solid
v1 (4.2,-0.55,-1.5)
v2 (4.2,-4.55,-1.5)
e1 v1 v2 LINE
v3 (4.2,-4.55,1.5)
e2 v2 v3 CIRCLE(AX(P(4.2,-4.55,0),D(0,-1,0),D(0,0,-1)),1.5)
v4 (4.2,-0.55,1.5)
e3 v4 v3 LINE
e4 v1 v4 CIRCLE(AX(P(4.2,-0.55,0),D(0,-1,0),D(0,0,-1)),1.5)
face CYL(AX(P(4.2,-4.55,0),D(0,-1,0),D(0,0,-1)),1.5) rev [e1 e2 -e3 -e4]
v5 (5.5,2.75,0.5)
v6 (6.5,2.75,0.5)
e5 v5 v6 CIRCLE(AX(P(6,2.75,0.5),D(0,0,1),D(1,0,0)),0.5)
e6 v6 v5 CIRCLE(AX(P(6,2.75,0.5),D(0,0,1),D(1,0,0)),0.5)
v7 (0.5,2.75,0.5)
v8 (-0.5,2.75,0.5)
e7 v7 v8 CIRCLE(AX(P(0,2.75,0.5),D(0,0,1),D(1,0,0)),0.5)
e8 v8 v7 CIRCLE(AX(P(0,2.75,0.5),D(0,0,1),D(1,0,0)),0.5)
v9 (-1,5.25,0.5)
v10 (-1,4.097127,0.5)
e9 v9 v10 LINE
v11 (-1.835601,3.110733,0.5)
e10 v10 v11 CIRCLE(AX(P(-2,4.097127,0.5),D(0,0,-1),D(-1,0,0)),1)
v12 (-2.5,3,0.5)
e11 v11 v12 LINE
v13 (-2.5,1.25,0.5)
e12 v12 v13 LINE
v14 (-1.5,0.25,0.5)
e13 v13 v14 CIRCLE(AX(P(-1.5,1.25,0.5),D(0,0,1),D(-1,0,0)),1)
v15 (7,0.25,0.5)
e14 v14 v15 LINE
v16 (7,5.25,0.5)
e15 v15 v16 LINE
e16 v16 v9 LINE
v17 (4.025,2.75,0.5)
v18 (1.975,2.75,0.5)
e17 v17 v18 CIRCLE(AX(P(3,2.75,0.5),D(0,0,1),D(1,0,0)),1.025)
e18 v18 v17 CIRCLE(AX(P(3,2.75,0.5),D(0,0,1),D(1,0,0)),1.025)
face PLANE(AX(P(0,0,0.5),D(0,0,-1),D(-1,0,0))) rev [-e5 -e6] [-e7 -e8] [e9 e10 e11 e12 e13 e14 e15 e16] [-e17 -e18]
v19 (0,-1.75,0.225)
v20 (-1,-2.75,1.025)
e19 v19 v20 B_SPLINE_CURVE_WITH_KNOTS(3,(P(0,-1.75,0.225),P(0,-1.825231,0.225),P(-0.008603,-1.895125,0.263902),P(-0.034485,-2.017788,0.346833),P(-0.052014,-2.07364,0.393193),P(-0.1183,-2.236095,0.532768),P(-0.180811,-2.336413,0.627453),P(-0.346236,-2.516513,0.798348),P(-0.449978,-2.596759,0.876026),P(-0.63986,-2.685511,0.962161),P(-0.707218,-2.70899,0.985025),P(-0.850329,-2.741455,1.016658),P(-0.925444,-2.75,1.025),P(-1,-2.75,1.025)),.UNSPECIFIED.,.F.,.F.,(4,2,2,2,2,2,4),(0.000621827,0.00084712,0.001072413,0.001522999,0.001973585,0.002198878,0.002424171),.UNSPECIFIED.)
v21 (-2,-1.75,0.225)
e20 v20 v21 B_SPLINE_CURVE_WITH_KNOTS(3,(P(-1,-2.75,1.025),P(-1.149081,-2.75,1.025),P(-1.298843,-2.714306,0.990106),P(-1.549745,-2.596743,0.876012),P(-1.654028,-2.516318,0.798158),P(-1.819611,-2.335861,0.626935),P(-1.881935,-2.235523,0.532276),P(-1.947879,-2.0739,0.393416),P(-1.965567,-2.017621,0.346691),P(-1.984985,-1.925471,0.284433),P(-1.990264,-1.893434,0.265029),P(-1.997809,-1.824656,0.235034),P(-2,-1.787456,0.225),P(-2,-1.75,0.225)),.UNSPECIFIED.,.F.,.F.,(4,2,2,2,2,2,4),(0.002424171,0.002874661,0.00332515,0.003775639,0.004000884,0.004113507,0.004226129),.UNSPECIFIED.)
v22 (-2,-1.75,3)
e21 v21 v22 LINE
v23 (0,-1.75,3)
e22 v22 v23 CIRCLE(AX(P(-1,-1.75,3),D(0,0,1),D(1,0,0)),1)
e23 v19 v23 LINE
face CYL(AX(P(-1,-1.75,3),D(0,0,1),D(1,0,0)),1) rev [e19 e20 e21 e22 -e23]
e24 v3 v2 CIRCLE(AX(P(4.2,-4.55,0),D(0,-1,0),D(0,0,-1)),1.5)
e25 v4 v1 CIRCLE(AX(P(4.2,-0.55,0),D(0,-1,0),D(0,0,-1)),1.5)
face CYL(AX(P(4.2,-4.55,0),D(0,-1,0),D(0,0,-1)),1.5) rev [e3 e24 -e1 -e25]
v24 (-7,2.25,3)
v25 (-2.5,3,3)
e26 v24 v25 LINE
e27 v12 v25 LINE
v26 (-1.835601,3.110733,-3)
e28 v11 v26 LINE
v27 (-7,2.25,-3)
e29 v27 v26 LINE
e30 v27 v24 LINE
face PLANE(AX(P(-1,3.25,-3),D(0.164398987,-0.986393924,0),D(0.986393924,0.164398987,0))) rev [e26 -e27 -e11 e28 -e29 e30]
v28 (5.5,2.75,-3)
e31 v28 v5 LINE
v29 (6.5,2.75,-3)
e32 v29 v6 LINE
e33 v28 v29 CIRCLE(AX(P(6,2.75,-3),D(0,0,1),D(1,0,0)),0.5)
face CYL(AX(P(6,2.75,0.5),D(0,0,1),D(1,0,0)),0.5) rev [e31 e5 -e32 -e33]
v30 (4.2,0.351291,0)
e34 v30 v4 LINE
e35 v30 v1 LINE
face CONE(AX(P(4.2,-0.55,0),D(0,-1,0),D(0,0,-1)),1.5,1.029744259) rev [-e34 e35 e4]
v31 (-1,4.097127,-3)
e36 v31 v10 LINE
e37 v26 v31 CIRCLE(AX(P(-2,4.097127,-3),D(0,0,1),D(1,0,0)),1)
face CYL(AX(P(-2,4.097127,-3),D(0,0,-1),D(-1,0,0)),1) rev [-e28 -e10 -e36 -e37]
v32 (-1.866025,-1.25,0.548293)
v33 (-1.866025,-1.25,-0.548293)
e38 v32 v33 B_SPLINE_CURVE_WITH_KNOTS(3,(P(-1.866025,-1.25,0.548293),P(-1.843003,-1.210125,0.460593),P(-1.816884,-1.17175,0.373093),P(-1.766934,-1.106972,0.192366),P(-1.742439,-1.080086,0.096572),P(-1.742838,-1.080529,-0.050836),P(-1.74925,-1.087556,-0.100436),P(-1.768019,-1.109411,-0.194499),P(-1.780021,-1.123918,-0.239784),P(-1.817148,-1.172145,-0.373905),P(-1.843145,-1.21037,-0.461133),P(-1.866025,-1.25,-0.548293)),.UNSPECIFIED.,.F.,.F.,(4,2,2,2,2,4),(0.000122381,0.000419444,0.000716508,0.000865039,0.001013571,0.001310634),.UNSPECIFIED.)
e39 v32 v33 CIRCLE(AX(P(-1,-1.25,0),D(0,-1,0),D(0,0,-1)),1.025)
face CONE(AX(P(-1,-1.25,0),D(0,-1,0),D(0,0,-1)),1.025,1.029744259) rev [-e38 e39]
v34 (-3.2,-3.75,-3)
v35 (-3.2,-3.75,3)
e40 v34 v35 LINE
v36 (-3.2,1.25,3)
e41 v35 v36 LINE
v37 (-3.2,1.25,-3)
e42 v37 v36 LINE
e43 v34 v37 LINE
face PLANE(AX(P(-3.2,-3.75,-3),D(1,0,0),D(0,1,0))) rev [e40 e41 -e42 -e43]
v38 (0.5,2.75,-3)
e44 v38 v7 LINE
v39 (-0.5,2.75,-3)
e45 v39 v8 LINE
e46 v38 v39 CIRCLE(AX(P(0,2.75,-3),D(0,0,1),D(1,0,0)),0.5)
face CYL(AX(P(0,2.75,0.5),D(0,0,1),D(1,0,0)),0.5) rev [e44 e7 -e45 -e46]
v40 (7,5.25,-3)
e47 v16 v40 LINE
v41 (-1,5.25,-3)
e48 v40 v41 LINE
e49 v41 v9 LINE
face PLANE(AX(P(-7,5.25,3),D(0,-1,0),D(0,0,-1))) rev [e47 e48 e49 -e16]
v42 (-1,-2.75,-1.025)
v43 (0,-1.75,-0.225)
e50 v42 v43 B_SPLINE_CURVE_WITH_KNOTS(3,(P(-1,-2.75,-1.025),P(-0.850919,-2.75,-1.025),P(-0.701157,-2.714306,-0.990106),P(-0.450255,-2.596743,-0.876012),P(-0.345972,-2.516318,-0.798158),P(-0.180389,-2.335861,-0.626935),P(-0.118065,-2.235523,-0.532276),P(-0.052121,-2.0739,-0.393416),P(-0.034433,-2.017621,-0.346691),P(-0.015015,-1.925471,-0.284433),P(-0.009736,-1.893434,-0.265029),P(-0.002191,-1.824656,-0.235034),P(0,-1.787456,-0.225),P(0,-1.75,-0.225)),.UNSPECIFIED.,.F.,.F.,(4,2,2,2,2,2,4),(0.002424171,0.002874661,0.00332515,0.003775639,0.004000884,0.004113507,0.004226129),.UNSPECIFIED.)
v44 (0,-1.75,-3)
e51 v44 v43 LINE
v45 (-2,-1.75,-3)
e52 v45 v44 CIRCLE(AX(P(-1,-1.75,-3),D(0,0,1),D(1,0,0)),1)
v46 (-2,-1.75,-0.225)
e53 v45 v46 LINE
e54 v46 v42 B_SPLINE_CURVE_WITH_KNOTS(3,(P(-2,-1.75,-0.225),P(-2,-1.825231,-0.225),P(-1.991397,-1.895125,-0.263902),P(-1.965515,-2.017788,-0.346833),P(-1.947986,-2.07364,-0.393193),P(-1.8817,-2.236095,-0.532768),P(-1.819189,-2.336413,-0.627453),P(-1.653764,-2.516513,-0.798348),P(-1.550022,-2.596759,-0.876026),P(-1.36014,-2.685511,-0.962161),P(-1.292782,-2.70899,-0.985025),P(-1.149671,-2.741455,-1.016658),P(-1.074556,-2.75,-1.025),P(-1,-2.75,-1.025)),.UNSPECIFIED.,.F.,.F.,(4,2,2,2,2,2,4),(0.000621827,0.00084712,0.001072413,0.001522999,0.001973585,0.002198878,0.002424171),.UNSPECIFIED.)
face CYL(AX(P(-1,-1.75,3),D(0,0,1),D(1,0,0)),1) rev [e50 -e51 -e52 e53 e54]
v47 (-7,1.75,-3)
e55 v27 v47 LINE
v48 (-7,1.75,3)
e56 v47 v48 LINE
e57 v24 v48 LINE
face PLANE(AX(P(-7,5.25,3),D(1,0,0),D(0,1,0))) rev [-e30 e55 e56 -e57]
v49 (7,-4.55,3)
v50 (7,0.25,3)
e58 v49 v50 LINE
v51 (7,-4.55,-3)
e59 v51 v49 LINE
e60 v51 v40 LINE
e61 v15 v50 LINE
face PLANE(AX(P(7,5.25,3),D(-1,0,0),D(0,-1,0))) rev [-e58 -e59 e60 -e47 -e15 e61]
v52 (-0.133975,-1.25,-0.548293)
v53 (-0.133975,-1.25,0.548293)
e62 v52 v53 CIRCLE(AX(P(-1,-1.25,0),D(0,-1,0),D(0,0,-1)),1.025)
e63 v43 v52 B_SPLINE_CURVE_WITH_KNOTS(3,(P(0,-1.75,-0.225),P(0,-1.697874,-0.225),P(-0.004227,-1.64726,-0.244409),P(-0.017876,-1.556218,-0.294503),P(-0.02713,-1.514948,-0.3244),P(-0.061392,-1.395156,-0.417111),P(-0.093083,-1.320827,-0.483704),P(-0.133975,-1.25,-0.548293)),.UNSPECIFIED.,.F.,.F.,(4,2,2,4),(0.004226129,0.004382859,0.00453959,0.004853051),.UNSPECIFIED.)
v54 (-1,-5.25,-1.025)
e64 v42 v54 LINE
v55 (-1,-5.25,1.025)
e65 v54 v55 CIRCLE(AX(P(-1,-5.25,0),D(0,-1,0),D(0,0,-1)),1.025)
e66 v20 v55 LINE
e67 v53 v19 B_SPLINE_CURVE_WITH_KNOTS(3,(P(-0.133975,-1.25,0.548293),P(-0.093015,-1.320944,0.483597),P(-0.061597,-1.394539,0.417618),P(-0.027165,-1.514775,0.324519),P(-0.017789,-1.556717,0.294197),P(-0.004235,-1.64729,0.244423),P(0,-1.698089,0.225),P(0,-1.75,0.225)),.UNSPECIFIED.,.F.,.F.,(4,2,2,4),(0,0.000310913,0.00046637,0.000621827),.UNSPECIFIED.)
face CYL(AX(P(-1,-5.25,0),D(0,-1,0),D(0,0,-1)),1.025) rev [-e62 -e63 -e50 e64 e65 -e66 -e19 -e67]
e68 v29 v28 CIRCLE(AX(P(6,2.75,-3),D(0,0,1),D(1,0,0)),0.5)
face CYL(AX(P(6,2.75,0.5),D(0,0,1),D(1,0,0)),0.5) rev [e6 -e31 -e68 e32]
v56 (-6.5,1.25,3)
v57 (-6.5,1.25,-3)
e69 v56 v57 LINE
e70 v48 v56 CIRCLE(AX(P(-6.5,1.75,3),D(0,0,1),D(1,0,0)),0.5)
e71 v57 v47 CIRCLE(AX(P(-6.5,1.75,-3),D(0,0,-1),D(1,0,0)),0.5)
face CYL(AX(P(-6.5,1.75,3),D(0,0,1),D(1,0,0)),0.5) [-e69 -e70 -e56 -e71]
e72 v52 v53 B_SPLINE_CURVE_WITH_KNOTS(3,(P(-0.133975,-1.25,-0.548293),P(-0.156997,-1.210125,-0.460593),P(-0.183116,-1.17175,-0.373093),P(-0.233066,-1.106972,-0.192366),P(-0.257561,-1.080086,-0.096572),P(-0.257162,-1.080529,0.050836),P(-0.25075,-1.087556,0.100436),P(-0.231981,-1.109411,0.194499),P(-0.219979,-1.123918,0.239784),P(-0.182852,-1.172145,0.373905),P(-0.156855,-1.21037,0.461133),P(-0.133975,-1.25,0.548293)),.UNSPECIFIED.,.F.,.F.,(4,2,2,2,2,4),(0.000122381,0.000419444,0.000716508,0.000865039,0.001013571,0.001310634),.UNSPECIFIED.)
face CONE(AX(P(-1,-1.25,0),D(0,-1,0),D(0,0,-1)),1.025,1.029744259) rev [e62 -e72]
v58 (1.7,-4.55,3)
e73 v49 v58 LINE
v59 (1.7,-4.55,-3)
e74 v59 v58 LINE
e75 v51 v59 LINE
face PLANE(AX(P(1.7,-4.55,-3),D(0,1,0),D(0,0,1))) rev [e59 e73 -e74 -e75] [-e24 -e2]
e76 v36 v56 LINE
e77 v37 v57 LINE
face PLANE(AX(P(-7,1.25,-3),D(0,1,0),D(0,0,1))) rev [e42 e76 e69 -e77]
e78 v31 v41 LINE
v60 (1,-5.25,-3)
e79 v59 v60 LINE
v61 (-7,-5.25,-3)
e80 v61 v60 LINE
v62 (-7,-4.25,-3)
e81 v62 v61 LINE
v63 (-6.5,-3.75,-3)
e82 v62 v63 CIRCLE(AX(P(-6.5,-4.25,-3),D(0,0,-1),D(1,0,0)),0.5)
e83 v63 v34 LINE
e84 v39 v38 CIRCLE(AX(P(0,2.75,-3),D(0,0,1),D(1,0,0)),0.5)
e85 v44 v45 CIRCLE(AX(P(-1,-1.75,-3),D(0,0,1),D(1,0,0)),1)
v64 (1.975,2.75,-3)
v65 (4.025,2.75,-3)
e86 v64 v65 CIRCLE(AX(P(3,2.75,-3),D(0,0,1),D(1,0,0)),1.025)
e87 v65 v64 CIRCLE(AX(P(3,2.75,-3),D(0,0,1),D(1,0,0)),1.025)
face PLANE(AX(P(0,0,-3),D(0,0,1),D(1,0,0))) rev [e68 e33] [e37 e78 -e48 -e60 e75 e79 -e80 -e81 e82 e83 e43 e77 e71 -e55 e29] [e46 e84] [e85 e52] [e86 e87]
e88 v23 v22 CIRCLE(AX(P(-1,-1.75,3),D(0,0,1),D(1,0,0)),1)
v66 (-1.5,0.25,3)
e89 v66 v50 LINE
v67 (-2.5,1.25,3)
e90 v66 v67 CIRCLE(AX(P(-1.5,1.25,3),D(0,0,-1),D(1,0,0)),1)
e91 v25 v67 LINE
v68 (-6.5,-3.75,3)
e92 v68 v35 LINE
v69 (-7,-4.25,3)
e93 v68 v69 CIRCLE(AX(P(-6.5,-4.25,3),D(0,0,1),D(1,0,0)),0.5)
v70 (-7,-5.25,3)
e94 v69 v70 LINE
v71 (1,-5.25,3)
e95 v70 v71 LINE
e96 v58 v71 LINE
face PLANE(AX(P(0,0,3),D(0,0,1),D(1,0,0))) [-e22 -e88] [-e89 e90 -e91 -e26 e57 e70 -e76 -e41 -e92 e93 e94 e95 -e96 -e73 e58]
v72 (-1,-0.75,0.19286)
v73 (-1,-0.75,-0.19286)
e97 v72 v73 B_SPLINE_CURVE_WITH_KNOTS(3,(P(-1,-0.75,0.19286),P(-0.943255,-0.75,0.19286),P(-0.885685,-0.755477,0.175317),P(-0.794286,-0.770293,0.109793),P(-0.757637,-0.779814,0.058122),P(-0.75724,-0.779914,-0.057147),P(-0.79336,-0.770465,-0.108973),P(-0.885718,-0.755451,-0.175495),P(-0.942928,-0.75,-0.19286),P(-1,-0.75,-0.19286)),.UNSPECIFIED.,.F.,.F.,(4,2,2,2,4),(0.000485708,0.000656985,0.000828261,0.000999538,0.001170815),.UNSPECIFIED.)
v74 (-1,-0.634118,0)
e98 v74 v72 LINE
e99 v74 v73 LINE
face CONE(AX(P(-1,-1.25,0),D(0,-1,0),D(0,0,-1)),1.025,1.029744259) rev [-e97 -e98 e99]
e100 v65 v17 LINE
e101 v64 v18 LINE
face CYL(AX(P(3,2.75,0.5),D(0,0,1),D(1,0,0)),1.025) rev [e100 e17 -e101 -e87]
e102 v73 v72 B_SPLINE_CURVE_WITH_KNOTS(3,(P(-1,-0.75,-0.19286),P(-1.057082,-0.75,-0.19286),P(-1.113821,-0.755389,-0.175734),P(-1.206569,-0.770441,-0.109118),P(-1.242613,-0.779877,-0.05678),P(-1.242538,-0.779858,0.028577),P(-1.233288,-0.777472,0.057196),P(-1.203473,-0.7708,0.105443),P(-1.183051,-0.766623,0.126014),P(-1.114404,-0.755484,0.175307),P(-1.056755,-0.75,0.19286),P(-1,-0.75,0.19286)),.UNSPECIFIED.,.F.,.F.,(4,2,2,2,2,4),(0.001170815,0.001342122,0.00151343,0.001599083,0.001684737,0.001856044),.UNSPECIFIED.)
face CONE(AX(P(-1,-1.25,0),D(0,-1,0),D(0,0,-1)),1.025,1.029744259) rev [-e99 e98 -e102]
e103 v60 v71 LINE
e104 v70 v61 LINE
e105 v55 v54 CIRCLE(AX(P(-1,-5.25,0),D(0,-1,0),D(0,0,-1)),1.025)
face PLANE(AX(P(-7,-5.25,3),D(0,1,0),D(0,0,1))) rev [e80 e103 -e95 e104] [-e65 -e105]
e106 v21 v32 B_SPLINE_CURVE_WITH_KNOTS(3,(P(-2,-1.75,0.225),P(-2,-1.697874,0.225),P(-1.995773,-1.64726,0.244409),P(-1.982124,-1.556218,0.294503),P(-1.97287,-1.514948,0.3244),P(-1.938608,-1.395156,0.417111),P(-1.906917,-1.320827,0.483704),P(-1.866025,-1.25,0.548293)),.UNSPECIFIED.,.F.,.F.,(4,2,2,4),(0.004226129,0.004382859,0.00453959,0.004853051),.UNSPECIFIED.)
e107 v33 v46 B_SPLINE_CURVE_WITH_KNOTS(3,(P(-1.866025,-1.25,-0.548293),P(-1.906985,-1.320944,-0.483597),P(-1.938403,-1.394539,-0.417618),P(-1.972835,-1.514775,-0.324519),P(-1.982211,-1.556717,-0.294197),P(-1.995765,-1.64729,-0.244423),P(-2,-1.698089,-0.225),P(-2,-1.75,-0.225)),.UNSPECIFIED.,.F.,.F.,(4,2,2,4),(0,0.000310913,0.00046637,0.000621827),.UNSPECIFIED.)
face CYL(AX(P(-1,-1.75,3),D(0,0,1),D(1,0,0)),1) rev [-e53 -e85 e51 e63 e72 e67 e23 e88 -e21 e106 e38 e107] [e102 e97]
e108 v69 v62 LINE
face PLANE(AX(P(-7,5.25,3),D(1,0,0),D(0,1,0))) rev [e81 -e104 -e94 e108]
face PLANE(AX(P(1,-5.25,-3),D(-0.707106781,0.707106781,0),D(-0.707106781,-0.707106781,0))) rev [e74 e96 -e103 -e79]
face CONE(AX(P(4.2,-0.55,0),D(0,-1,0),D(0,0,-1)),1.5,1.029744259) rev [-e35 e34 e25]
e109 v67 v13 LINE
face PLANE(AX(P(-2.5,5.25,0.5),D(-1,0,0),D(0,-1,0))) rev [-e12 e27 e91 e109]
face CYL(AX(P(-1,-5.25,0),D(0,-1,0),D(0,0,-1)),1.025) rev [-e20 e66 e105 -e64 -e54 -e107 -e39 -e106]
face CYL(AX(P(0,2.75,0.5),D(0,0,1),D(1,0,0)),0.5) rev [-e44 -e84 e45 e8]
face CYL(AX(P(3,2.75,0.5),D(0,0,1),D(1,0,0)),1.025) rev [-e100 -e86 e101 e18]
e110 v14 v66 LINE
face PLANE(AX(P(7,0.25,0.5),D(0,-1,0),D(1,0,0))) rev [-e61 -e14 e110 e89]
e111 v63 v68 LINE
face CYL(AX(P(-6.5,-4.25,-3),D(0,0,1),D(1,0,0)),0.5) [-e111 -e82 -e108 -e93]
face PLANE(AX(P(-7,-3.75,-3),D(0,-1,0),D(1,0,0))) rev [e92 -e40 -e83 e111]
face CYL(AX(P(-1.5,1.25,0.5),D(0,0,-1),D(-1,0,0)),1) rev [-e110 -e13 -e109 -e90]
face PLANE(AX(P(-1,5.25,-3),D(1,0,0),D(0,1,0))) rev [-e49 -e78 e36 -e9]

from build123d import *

# Parameters (mm, degrees)
SKETCH1_W                    = 14
SKETCH1_H                    = 10.5
BOSS_EXTRUDE1_DEPTH          = 3
SKETCH2_W                    = 9.5
SKETCH2_H                    = 5
CUT_EXTRUDE1_DEPTH           = 2.5
CUT_EXTRUDE2_DEPTH           = 11.609547587
FILLET1_R                    = 1
SKETCH4_W                    = 3.8
SKETCH4_H                    = 5
CUT_EXTRUDE3_DEPTH           = 11.609547587
M2_5_TAPPED_HOLE1_D          = 2.05
F_1_0_1_DIAMETER_HOLE1_D     = 1
F_2_0_2_DIAMETER_HOLE1_D     = 2
CUT_EXTRUDE4_DEPTH           = 11.609547587
F_3_0_3_DIAMETER_HOLE1_D     = 3
F_3_0_3_DIAMETER_HOLE1_DEPTH = 4
F_3_0_3_DIAMETER_HOLE1_TIP   = 0.901290929
FILLET2_R                    = 0.5
M2_5_TAPPED_HOLE2_D          = 2.05
M2_5_TAPPED_HOLE2_DEPTH      = 4
M2_5_TAPPED_HOLE2_TIP        = 0.615882135


with BuildPart() as part:
    # Sketch1 → Boss-Extrude1 (new, symmetric)
    with BuildSketch(Plane.XY):
        Rectangle(SKETCH1_W, SKETCH1_H)
    extrude(amount=BOSS_EXTRUDE1_DEPTH, both=True)

    # Sketch2 → Cut-Extrude1 (cut)
    with BuildSketch(Plane.XY.offset(3)):
        with Locations((2.25, 2.75)):
            Rectangle(SKETCH2_W, SKETCH2_H)
    extrude(amount=-CUT_EXTRUDE1_DEPTH, mode=Mode.SUBTRACT)

    # Sketch3 → Cut-Extrude2 (cut, through all)
    with BuildSketch(Plane.XY.offset(3)):
        Polygon((-7, 5.25), (-1, 5.25), (-1, 3.25), (-7, 2.25), align=None)
    extrude(amount=-CUT_EXTRUDE2_DEPTH, mode=Mode.SUBTRACT)

    # Fillet1
    fillet1_edges = [part.edges().sort_by_distance(p)[0] for p in [
        (-2.5, 0.25, 1.75),
        (-1, 3.25, -1.25),
    ]]
    fillet(fillet1_edges, radius=FILLET1_R)

    # Sketch4 → Cut-Extrude3 (cut, through all)
    with BuildSketch(Plane.XY.offset(3)):
        with Locations((-5.1, -1.25)):
            Rectangle(SKETCH4_W, SKETCH4_H)
    extrude(amount=-CUT_EXTRUDE3_DEPTH, mode=Mode.SUBTRACT)

    # M2.5 Tapped Hole1 (through all)
    with Locations(Plane.XY.offset(0.5)):
        with Locations((3, 2.75)):
            Hole(M2_5_TAPPED_HOLE1_D / 2)

    # Ø1.0 (1) Diameter Hole1 (through all)
    with Locations(Plane.XY.offset(0.5)):
        with Locations((0, 2.75), (6, 2.75)):
            Hole(F_1_0_1_DIAMETER_HOLE1_D / 2)

    # Ø2.0 (2) Diameter Hole1 (through all)
    with Locations(Plane.XY.offset(3)):
        with Locations((-1, -1.75)):
            Hole(F_2_0_2_DIAMETER_HOLE1_D / 2)

    # Sketch15 → Cut-Extrude4 (cut, through all)
    with BuildSketch(Plane.XY.offset(3)):
        Polygon((7, -5.25), (1, -5.25), (1.7, -4.55), (7, -4.55), align=None)
    extrude(amount=-CUT_EXTRUDE4_DEPTH, mode=Mode.SUBTRACT)

    # Ø3.0 (3) Diameter Hole1
    with Locations(Plane(origin=(0, -4.55, 0), x_dir=(-1, 0, 0), z_dir=(0, -1, 0))):
        with Locations((-4.2, 0)):
            Hole(F_3_0_3_DIAMETER_HOLE1_D / 2, depth=F_3_0_3_DIAMETER_HOLE1_DEPTH)
            with Locations((0, 0, -(F_3_0_3_DIAMETER_HOLE1_DEPTH + F_3_0_3_DIAMETER_HOLE1_TIP / 2))):  # 118° drill point
                Cone(0, F_3_0_3_DIAMETER_HOLE1_D / 2, F_3_0_3_DIAMETER_HOLE1_TIP, mode=Mode.SUBTRACT)

    # Fillet2
    fillet2_edges = [part.edges().sort_by_distance(p)[0] for p in [
        (-7, -3.75, 0),
        (-7, 1.25, 0),
    ]]
    fillet(fillet2_edges, radius=FILLET2_R)

    # M2.5 Tapped Hole2
    with Locations(Plane(origin=(0, -5.25, 0), x_dir=(-1, 0, 0), z_dir=(0, -1, 0))):
        with Locations((1, 0)):
            Hole(M2_5_TAPPED_HOLE2_D / 2, depth=M2_5_TAPPED_HOLE2_DEPTH)
            with Locations((0, 0, -(M2_5_TAPPED_HOLE2_DEPTH + M2_5_TAPPED_HOLE2_TIP / 2))):  # 118° drill point
                Cone(0, M2_5_TAPPED_HOLE2_D / 2, M2_5_TAPPED_HOLE2_TIP, mode=Mode.SUBTRACT)


solid = part.part
